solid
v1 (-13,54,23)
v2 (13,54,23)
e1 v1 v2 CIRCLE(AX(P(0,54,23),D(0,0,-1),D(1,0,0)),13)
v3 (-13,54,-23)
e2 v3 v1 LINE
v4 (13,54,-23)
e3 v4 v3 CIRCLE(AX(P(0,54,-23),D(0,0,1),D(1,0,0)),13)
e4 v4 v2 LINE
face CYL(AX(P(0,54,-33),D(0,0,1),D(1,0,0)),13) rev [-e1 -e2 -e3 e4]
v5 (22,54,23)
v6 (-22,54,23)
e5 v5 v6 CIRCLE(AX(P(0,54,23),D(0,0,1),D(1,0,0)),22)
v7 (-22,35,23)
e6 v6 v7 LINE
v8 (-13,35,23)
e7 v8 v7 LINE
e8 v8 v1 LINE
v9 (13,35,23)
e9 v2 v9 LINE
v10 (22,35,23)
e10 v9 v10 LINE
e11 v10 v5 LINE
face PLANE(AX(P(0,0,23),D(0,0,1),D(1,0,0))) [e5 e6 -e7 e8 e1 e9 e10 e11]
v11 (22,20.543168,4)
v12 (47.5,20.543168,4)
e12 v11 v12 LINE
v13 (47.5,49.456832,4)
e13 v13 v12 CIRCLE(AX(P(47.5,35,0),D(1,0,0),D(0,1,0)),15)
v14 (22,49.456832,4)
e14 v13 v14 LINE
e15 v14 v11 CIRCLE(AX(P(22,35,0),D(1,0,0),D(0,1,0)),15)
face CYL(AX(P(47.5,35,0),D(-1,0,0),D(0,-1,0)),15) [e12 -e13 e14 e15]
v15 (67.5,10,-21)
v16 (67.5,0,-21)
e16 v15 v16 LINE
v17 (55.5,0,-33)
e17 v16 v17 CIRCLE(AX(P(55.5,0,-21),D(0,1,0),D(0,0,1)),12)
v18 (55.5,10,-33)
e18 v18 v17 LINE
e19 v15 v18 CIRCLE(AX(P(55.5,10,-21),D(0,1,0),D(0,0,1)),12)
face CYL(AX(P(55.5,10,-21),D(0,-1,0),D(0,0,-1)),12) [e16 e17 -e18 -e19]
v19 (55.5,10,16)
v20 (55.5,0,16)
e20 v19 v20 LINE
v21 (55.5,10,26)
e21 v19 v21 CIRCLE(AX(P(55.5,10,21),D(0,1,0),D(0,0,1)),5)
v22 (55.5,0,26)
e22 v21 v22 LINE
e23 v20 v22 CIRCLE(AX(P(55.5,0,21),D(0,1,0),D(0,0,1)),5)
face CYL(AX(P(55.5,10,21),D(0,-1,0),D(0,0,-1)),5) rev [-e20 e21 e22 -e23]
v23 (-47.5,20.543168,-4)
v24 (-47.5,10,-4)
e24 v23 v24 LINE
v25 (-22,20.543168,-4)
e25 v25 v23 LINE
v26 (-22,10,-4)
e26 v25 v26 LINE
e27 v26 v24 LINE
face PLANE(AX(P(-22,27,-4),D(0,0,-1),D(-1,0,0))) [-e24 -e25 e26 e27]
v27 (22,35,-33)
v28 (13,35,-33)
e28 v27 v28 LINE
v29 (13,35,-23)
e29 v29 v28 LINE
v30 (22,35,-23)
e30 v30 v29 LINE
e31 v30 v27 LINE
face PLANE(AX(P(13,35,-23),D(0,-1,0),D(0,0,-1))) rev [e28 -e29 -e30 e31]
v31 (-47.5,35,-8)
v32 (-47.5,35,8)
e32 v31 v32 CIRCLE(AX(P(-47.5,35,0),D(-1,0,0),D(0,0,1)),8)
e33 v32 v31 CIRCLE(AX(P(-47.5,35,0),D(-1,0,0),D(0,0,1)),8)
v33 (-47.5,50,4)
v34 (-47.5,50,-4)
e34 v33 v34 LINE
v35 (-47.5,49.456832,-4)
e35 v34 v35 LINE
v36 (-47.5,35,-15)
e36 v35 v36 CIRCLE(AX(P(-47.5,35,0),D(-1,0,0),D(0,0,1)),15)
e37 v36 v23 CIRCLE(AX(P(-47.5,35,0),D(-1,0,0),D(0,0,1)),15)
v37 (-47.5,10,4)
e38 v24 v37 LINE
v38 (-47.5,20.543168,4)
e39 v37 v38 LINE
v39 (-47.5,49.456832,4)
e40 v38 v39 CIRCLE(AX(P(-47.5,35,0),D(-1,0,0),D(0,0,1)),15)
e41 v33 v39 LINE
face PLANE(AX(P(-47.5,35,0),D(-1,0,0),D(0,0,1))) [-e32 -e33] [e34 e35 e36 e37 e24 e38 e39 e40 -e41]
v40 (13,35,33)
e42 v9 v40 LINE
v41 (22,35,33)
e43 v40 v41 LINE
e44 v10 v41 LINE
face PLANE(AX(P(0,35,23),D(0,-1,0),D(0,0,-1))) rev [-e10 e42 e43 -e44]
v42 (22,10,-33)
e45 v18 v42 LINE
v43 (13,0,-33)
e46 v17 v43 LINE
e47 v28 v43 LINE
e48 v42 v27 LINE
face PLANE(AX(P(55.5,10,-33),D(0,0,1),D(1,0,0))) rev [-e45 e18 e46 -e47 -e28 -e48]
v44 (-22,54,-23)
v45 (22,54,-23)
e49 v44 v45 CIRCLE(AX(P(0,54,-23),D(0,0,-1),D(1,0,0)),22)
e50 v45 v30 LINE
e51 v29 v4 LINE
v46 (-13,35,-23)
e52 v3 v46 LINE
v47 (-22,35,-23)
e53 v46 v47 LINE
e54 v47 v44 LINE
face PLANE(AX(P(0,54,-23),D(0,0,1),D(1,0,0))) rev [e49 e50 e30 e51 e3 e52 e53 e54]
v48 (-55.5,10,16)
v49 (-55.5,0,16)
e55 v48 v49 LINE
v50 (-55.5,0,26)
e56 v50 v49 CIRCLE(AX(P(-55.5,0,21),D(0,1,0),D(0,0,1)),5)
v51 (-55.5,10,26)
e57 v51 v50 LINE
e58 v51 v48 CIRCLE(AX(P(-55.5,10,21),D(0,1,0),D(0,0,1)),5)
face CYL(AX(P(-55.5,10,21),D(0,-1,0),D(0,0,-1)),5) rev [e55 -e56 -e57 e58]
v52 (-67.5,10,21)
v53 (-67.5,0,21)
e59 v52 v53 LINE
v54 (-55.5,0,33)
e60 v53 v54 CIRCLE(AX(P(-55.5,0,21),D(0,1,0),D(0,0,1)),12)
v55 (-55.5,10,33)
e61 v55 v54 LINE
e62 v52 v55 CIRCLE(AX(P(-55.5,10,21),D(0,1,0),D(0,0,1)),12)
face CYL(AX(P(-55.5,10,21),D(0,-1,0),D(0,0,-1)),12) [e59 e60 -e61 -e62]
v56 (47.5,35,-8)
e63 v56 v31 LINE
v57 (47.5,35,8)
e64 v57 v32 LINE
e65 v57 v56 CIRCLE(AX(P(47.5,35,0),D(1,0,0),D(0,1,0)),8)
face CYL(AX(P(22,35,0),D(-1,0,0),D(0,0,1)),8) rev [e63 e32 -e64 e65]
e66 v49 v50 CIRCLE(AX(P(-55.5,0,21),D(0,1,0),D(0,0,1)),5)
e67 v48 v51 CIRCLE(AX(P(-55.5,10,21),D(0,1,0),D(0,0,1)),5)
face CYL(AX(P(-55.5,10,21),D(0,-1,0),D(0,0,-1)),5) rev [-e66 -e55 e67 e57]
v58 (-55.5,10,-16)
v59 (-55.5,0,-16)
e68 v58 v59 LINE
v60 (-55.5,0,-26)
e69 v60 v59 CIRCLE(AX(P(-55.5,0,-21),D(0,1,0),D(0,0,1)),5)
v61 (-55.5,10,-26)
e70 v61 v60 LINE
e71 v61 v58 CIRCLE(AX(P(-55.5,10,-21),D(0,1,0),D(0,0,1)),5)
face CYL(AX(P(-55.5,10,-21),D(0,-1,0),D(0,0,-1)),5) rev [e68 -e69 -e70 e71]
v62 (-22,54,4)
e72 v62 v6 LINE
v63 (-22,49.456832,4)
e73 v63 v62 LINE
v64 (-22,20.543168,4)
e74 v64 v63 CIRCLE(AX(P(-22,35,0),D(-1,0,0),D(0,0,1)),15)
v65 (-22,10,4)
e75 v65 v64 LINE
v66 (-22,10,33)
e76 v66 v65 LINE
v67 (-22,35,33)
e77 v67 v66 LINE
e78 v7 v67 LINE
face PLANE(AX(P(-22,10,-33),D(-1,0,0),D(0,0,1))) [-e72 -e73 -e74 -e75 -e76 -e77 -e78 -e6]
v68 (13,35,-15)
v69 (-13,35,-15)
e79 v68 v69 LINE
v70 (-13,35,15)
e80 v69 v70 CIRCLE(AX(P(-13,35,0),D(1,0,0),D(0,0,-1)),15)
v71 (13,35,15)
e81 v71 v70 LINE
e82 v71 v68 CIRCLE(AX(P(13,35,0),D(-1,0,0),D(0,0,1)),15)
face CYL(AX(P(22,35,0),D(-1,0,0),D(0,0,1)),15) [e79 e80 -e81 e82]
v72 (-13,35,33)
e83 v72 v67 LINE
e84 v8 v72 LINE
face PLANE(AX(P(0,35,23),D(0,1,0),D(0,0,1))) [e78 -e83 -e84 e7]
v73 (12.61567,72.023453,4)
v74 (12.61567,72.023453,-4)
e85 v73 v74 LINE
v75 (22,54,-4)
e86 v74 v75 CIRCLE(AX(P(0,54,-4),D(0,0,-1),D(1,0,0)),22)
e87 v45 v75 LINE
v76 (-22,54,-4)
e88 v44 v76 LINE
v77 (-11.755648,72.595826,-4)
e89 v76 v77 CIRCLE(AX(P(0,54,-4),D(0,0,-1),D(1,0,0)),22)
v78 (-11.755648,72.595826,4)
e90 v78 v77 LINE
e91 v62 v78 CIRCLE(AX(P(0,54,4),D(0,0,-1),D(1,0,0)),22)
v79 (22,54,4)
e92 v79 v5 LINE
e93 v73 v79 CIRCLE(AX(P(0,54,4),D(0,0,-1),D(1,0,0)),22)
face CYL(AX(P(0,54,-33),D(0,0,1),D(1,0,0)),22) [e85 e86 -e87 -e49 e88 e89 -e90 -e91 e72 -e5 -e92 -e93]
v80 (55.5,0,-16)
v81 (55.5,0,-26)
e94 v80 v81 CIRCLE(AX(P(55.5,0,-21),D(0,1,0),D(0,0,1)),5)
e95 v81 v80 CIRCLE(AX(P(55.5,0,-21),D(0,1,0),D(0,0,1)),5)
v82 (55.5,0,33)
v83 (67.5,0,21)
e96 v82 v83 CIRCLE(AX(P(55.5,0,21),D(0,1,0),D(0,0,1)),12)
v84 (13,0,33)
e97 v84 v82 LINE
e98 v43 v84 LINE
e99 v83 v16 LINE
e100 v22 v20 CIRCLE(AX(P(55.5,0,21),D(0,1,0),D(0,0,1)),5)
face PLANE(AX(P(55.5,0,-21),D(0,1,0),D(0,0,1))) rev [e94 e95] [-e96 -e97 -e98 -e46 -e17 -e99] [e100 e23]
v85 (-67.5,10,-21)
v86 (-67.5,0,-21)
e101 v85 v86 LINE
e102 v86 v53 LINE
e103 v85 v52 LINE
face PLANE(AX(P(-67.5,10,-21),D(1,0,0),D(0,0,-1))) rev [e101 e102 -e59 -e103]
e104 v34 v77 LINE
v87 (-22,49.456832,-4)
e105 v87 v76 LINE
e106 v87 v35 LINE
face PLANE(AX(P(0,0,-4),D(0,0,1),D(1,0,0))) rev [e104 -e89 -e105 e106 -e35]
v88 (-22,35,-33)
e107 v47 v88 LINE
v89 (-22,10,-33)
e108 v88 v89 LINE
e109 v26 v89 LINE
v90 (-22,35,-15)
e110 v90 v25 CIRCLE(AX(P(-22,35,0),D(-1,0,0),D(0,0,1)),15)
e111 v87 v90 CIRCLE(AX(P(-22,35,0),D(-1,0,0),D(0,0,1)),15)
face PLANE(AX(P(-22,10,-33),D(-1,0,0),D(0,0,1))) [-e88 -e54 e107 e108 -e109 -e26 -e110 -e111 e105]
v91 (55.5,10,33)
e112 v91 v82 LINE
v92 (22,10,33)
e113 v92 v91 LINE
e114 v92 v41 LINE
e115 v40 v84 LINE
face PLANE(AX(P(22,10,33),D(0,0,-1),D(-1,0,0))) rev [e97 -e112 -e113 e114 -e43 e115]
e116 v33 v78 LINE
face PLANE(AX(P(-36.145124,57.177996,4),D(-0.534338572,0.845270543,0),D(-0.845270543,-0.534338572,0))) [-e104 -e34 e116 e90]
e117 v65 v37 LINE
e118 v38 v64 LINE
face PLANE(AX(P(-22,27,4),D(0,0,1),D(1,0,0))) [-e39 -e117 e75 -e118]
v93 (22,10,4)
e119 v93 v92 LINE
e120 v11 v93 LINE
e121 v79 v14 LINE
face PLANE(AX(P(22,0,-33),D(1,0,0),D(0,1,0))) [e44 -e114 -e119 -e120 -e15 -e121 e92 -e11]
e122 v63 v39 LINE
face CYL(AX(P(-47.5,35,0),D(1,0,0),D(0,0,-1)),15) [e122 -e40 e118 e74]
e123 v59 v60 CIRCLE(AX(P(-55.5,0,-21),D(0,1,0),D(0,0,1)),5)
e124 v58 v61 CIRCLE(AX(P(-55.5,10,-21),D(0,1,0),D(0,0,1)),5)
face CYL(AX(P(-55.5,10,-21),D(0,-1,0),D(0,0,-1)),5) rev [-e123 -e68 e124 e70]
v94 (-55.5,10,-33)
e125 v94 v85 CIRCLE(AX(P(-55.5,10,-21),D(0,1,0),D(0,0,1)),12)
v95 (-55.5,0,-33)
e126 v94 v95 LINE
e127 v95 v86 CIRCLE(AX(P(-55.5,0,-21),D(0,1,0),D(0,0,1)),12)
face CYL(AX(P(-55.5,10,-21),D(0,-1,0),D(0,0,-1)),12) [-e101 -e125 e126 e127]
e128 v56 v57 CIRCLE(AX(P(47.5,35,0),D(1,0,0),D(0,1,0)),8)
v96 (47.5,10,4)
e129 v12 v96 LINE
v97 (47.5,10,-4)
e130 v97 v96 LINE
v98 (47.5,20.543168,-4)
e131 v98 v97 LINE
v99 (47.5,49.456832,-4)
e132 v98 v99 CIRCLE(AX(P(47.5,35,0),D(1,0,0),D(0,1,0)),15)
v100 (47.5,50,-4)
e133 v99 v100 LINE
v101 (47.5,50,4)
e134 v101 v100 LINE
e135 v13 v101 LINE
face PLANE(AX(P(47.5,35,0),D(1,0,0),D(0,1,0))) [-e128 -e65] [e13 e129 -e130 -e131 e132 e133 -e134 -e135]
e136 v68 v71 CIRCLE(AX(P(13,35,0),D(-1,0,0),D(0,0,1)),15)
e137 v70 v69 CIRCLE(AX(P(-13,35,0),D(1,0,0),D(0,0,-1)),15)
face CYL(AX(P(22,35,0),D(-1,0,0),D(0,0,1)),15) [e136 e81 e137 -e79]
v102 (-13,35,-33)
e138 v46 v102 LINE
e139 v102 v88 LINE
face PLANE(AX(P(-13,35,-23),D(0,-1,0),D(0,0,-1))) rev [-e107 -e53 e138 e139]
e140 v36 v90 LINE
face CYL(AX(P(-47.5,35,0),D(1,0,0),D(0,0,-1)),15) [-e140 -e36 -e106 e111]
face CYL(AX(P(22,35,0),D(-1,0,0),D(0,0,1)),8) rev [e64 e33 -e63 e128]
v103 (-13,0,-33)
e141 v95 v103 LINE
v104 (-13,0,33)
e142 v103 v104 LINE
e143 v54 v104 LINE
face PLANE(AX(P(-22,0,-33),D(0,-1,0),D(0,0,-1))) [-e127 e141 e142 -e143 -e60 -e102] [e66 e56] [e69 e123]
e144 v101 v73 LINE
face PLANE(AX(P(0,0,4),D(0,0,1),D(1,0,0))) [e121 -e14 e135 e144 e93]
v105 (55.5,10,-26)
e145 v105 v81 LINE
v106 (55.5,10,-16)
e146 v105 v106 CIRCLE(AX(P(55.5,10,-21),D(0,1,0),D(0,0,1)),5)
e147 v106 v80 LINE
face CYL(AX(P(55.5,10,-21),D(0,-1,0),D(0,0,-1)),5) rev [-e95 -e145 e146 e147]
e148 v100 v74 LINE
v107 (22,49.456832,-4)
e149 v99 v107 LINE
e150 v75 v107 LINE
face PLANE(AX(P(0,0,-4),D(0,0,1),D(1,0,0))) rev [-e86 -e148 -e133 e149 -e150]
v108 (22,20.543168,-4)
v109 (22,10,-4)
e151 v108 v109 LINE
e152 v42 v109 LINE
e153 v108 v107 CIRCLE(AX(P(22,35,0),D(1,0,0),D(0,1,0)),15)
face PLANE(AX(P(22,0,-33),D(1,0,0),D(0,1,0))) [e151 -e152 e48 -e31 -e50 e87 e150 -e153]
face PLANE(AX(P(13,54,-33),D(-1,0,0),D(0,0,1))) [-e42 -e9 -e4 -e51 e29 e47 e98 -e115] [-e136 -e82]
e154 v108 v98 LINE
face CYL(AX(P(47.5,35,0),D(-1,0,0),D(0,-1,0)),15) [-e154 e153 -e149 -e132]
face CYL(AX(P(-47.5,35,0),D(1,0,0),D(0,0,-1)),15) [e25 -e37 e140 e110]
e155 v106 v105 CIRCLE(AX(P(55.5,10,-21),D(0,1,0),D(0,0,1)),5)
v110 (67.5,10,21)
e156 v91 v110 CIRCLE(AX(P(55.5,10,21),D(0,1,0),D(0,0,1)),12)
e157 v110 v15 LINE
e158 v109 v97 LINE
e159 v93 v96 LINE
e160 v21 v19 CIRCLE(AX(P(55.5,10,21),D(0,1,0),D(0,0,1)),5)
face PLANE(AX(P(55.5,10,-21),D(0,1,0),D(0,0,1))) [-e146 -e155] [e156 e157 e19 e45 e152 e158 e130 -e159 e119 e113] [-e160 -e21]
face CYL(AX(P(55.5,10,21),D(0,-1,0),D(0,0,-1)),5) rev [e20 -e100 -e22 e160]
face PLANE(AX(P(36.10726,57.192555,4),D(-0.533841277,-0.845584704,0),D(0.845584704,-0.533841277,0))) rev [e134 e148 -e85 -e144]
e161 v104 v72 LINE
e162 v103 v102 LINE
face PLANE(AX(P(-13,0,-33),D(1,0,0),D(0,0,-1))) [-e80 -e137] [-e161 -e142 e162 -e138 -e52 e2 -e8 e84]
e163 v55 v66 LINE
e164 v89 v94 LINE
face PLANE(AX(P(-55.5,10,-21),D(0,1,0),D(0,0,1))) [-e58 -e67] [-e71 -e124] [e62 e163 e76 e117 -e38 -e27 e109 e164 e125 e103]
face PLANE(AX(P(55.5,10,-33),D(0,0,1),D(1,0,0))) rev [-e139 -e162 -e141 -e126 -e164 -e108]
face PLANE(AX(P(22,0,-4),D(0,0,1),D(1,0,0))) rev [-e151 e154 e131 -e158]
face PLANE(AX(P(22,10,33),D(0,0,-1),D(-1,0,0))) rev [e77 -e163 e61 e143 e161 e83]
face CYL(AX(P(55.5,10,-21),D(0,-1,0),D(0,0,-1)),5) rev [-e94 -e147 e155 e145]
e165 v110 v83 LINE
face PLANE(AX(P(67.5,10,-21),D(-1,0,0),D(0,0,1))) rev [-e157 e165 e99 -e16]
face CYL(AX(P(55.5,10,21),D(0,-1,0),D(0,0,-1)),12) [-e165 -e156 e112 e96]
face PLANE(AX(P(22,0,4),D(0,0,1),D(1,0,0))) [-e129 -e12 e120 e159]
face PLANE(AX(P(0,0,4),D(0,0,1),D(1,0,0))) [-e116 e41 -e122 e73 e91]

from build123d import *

# Parameters (mm, degrees)
BASE_PLATE_SKETCH_R      = 5
BASE_PLATE_DEPTH         = 10
BASE_PLATE_2_DEPTH       = 10
HOUSING_BLOCK_DEPTH      = 66
ARCH_OPENING_CUT_DEPTH   = 10
HOUSING_START            = -10
HOUSING_RELIEF_CUT_DEPTH = 10
PIVOT_BARREL_SKETCH_R    = 15
PIVOT_BARREL_SKETCH_R_2  = 8
PIVOT_BARREL_DEPTH       = 44
PIVOT_BORE_SKETCH_R      = 8
PIVOT_BORE_16_DEPTH      = 44
SIDE_START               = 25.5
SIDE_BOSS_A_SKETCH_R     = 15
SIDE_BOSS_A_SKETCH_R_2   = 8
SIDE_BOSS_A_DEPTH        = 25.5
SIDE_BOSS_B_SKETCH_R     = 15
SIDE_BOSS_B_SKETCH_R_2   = 8
SIDE_BOSS_B_DEPTH        = 25.5
SIDE_WEB_B_SKETCH_W      = 8
SIDE_WEB_B_SKETCH_H      = 17
SIDE_WEB_B_DEPTH         = 25.5
SIDE_WEB_A_SKETCH_W      = 8
SIDE_WEB_A_SKETCH_H      = 17
SIDE_WEB_A_DEPTH         = 25.5
GUSSET_RIB_DEPTH         = 4


with BuildPart() as part:
    # Base Plate Sketch → Base Plate (new body)
    with BuildSketch(Plane(origin=(0, 0, 0), x_dir=(1, 0, 0), z_dir=(0, 1, 0))):
        with BuildLine():
            Line((-55.5, 33), (-22, 33))
            Line((-22, 33), (-22, -33))
            Line((-22, -33), (-55.5, -33))
            ThreePointArc((-55.5, -33), (-63.985281374, -29.485281374), (-67.5, -21))
            Line((-67.5, -21), (-67.5, 21))
            ThreePointArc((-67.5, 21), (-63.985281374, 29.485281374), (-55.5, 33))
        make_face()
        with Locations(Location((-55.5, 21, 0), (0, 0, 270))):
            Circle(BASE_PLATE_SKETCH_R, mode=Mode.SUBTRACT)
        with Locations(Location((-55.5, -21, 0), (0, 0, 270))):
            Circle(BASE_PLATE_SKETCH_R, mode=Mode.SUBTRACT)
    extrude(amount=BASE_PLATE_DEPTH)



with BuildPart() as body_2:
    # Base Plate Sketch → Base Plate 2 (new body)
    with BuildSketch(Plane(origin=(0, 0, 0), x_dir=(1, 0, 0), z_dir=(0, 1, 0))):
        with BuildLine():
            Line((67.5, 21), (67.5, -21))
            ThreePointArc((67.5, -21), (63.985281374, -29.485281374), (55.5, -33))
            Line((55.5, -33), (22, -33))
            Line((22, -33), (22, 33))
            Line((22, 33), (55.5, 33))
            ThreePointArc((55.5, 33), (63.985281374, 29.485281374), (67.5, 21))
        make_face()
        with Locations(Location((55.5, 21, 0), (0, 0, 270))):
            Circle(BASE_PLATE_SKETCH_R, mode=Mode.SUBTRACT)
        with Locations(Location((55.5, -21, 0), (0, 0, 270))):
            Circle(BASE_PLATE_SKETCH_R, mode=Mode.SUBTRACT)
    extrude(amount=BASE_PLATE_2_DEPTH)


with BuildPart() as part_1:
    add(part.part)

    add(body_2.part)  # Housing Block merges body 2
    # Housing Block Sketch → Housing Block (add)
    with BuildSketch(Plane.XY.offset(33)):
        with BuildLine():
            Line((-22, 54), (-22, 10))
            Line((-22, 10), (-22, 0))
            Line((-22, 0), (-13, 0))
            Line((-13, 0), (-13, 54))
            ThreePointArc((-13, 54), (0, 67), (13, 54))
            Line((13, 54), (13, 0))
            Line((13, 0), (22, 0))
            Line((22, 0), (22, 54))
            ThreePointArc((22, 54), (0, 76), (-22, 54))
        make_face()
    extrude(amount=-HOUSING_BLOCK_DEPTH)

    # Arch Opening Sketch → Arch Opening Cut (cut)
    with BuildSketch(Plane.XY.offset(33)):
        with BuildLine():
            Line((13, 54), (13, 35))
            Line((13, 35), (22, 35))
            Line((22, 35), (22, 54))
            ThreePointArc((22, 54), (0, 76), (-22, 54))
            Line((-22, 54), (-22, 35))
            Line((-22, 35), (-13, 35))
            Line((-13, 35), (-13, 54))
            ThreePointArc((-13, 54), (0, 67), (13, 54))
        make_face()
    extrude(amount=-ARCH_OPENING_CUT_DEPTH, mode=Mode.SUBTRACT)

    # Housing Relief Sketch → Housing Relief Cut (cut)
    with BuildSketch(Plane(origin=(0, 0, -33), x_dir=(-1, 0, 0), z_dir=(0, 0, -1)).offset(HOUSING_START)):
        with BuildLine():
            Line((-13, 35), (-22, 35))
            Line((-22, 35), (-22, 54))
            ThreePointArc((-22, 54), (0, 76), (22, 54))
            Line((22, 54), (22, 35))
            Line((22, 35), (13, 35))
            Line((13, 35), (13, 54))
            ThreePointArc((13, 54), (0, 67), (-13, 54))
            Line((-13, 54), (-13, 35))
        make_face()
    extrude(amount=HOUSING_RELIEF_CUT_DEPTH, mode=Mode.SUBTRACT)

    # Pivot Barrel Sketch → Pivot Barrel (add)
    with BuildSketch(Plane.ZY.offset(22)):
        with Locations((0, 35)):
            Circle(PIVOT_BARREL_SKETCH_R)
        with Locations((0, 35)):
            Circle(PIVOT_BARREL_SKETCH_R_2, mode=Mode.SUBTRACT)
    extrude(amount=-PIVOT_BARREL_DEPTH)

    # Pivot Bore Sketch → Pivot Bore Ø16 (cut)
    with BuildSketch(Plane.ZY.offset(22)):
        with Locations((0, 35)):
            Circle(PIVOT_BORE_SKETCH_R)
    extrude(amount=-PIVOT_BORE_16_DEPTH, mode=Mode.SUBTRACT)

    # Side Boss A Sketch → Side Boss A (add)
    with BuildSketch(Plane.ZY.offset(22).offset(SIDE_START)):
        with Locations((0, 35)):
            Circle(SIDE_BOSS_A_SKETCH_R)
        with Locations((0, 35)):
            Circle(SIDE_BOSS_A_SKETCH_R_2, mode=Mode.SUBTRACT)
    extrude(amount=-SIDE_BOSS_A_DEPTH)

    # Side Boss B Sketch → Side Boss B (add)
    with BuildSketch(Plane(origin=(22, 0, 0), x_dir=(0, 0, -1), z_dir=(1, 0, 0))):
        with Locations(Location((0, 35, 0), (0, 0, 180))):
            Circle(SIDE_BOSS_B_SKETCH_R)
        with Locations(Location((0, 35, 0), (0, 0, 180))):
            Circle(SIDE_BOSS_B_SKETCH_R_2, mode=Mode.SUBTRACT)
    extrude(amount=SIDE_BOSS_B_DEPTH)

    # Side Web B Sketch → Side Web B (add)
    with BuildSketch(Plane(origin=(47.5, 0, 0), x_dir=(0, 0, -1), z_dir=(1, 0, 0))):
        with Locations((0, 18.5)):
            Rectangle(SIDE_WEB_B_SKETCH_W, SIDE_WEB_B_SKETCH_H)
    extrude(amount=-SIDE_WEB_B_DEPTH)

    # Side Web A Sketch → Side Web A (add)
    with BuildSketch(Plane.ZY.offset(47.5)):
        with Locations((0, 18.5)):
            Rectangle(SIDE_WEB_A_SKETCH_W, SIDE_WEB_A_SKETCH_H)
    extrude(amount=-SIDE_WEB_A_DEPTH)

    # Gusset Rib Sketch → Gusset Rib (add, symmetric)
    with BuildSketch(Plane.XY):
        with BuildLine():
            Line((-11.755648115, 72.595825806), (-47.5, 50))
            Line((-47.5, 50), (-47.5, 44))
            Line((-47.5, 44), (-22, 44))
            Line((-22, 44), (-22, 54))
            ThreePointArc((-22, 54), (-19.269461053, 64.615454335), (-11.755648115, 72.595825806))
        make_face()
        with BuildLine():
            Line((47.5, 50), (12.615670058, 72.023453304))
            ThreePointArc((12.615670058, 72.023453304), (19.513389522, 64.16009987), (22, 54))
            Line((22, 54), (22, 44))
            Line((22, 44), (47.5, 44))
            Line((47.5, 44), (47.5, 50))
        make_face()
    extrude(amount=GUSSET_RIB_DEPTH, both=True)


solid = part_1.part
